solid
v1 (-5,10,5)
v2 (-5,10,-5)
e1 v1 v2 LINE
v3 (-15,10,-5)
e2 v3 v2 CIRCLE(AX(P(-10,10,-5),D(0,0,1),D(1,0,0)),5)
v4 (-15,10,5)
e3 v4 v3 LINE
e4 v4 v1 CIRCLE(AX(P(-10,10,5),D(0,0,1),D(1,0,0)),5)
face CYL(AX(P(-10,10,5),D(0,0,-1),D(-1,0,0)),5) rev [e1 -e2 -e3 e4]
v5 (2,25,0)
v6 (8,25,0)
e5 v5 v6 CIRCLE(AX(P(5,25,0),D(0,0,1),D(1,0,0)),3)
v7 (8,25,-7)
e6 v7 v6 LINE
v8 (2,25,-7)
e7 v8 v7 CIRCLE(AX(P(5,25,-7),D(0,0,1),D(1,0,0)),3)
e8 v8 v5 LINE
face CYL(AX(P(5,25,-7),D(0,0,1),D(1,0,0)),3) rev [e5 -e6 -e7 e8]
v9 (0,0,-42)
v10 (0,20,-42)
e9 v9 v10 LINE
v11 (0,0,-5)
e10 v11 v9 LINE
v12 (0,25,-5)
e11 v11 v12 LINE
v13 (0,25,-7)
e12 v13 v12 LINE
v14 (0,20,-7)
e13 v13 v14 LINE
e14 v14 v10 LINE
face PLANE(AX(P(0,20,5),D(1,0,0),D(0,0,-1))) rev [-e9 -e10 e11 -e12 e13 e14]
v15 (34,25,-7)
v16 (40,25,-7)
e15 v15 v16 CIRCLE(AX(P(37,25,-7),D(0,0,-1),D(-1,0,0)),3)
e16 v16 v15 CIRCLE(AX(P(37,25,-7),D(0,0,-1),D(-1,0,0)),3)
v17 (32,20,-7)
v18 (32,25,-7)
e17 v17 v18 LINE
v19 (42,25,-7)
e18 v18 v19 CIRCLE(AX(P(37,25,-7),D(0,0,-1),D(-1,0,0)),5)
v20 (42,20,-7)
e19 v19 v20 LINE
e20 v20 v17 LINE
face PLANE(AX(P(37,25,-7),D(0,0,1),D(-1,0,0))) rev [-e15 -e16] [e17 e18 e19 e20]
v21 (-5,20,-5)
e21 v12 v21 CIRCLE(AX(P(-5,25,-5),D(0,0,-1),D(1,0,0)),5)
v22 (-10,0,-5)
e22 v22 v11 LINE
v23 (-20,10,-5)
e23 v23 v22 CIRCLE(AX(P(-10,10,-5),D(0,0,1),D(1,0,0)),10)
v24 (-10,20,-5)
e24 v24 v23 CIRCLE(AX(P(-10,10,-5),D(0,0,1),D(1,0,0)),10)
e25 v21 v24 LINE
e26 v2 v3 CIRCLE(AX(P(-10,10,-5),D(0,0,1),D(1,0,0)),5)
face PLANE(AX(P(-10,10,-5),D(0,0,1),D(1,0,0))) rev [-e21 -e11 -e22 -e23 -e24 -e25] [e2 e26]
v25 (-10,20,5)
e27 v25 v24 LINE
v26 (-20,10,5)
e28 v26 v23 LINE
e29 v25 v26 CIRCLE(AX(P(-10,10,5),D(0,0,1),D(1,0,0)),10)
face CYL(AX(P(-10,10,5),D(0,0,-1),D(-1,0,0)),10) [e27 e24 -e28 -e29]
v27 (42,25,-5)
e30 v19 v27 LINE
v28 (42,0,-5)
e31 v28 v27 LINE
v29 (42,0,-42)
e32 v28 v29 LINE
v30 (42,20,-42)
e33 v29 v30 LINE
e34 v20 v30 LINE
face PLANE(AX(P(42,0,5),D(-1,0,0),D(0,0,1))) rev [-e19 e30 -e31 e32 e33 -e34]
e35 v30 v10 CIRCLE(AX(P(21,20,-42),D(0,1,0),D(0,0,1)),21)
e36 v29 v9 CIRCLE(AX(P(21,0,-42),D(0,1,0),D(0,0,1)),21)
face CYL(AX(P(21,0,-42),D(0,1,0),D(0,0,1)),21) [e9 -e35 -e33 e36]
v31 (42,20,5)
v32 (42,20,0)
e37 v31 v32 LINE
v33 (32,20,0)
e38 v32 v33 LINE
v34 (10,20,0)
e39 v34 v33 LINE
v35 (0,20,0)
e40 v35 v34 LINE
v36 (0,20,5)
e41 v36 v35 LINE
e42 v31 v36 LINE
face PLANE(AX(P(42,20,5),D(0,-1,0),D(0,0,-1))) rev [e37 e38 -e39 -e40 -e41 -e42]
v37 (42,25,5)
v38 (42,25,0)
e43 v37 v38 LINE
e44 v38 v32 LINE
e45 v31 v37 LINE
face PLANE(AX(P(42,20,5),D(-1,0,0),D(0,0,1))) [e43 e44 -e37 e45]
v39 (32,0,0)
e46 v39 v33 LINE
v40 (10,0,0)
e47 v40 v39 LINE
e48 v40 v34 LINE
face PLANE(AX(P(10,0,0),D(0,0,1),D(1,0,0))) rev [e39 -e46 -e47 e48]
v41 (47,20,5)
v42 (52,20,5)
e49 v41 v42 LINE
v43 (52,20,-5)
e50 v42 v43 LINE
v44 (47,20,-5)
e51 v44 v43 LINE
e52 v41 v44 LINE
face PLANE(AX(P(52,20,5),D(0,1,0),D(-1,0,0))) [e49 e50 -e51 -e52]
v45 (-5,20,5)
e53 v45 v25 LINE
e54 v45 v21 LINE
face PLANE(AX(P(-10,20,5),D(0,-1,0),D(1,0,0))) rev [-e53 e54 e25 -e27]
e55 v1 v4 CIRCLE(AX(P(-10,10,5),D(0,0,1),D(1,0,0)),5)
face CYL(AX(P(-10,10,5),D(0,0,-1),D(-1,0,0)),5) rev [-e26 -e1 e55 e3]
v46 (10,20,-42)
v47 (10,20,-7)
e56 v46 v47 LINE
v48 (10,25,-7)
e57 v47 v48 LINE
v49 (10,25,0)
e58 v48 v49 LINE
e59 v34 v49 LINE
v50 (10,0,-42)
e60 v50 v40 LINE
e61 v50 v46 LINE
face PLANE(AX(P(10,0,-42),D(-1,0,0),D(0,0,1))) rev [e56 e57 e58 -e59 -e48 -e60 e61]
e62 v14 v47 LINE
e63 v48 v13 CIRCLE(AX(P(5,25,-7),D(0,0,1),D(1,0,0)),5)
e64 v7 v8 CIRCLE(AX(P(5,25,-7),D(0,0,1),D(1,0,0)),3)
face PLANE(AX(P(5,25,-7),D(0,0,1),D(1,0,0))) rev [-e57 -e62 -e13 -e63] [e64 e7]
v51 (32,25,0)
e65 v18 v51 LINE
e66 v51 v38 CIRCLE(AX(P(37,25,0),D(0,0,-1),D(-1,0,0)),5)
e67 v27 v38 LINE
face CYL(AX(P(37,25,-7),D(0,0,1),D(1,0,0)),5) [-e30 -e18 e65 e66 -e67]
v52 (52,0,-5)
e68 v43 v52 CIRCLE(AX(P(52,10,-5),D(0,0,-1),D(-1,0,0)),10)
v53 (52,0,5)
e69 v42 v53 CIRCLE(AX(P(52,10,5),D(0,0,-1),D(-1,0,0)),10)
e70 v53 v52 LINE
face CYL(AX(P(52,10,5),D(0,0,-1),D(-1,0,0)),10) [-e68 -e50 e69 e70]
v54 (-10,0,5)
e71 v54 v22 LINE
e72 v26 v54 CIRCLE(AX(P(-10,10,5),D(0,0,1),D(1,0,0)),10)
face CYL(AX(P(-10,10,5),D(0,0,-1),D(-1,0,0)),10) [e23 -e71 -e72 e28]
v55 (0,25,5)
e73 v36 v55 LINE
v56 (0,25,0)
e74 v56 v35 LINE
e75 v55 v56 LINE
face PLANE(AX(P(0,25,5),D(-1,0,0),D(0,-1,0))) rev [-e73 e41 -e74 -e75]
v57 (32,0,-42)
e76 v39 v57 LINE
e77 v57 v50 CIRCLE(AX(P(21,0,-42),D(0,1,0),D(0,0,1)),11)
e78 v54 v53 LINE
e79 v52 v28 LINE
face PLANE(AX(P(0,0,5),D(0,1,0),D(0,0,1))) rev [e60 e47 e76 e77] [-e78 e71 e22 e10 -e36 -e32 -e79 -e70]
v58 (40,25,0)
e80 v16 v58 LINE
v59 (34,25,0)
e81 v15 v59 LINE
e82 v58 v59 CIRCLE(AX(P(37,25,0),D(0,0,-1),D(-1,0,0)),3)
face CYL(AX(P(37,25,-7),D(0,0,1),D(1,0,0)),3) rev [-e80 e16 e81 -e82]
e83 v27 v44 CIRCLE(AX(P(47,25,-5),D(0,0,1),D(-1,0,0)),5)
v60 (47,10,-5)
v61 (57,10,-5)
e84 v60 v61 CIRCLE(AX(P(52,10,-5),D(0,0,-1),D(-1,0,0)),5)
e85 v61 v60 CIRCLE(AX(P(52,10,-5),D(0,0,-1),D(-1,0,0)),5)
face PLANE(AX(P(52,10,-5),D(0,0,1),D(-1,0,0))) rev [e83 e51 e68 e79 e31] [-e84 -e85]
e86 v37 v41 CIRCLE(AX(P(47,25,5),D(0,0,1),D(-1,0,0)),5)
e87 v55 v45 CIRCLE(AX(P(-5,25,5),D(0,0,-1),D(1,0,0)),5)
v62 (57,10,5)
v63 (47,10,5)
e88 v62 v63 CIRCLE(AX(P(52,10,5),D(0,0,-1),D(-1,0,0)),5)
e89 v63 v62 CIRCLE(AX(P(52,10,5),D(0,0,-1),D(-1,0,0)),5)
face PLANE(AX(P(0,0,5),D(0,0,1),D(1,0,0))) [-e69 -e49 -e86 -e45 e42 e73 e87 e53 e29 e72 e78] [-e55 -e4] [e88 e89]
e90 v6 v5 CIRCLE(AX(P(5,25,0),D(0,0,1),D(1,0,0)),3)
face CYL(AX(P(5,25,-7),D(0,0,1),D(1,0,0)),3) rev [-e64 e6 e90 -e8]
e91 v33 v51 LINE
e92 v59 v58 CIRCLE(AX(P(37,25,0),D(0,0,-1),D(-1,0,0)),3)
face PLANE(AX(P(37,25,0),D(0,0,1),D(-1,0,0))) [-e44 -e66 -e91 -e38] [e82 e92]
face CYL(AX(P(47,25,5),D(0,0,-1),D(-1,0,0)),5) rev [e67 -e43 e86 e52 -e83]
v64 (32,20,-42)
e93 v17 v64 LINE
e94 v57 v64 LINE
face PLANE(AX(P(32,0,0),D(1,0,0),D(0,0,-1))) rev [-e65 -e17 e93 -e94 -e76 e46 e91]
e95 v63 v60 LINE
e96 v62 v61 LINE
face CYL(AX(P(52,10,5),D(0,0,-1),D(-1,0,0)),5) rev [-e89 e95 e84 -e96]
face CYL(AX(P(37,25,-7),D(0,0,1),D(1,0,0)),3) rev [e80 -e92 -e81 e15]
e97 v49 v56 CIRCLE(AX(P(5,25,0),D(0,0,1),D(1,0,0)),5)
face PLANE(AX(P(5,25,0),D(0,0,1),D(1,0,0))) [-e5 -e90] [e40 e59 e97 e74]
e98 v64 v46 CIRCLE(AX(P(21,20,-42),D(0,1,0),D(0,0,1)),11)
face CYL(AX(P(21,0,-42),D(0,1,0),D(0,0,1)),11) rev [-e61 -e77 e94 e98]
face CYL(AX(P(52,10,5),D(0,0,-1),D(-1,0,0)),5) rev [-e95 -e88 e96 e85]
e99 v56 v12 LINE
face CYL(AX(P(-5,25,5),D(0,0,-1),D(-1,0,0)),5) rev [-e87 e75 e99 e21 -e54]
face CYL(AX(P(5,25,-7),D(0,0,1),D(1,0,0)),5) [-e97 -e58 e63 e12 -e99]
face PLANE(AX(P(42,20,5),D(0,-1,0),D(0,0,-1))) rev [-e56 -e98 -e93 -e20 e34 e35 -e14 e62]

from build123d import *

# Parameters (mm, degrees)
BASE_PLATE_SKETCH_W    = 42
BASE_PLATE_SKETCH_H    = 20
BASE_PLATE_DEPTH       = 5
CURVED_LOOP_BOSS_DEPTH = 20
LOOP_SLOT_CUT_DEPTH    = 79.31347266
LUG_SKETCH_R           = 3
LUG_BOSS_DEPTH         = 7
PIN_EYE_SKETCH_R       = 5
PIN_EYE_BOSS_DEPTH     = 5


with BuildPart() as part:
    # Base Plate Sketch → Base Plate (new body)
    with BuildSketch(Plane.XY):
        with Locations((21, 10)):
            Rectangle(BASE_PLATE_SKETCH_W, BASE_PLATE_SKETCH_H)
    extrude(amount=BASE_PLATE_DEPTH)

    # Curved Loop Sketch → Curved Loop Boss (add, through all)
    with BuildSketch(Plane(origin=(0, 20, 0), x_dir=(1, 0, 0), z_dir=(0, 1, 0))):
        with BuildLine():
            Line((0, 42), (0, 0))
            Line((0, 0), (42, 0))
            Line((42, 0), (42, 42))
            ThreePointArc((42, 42), (21, 63), (0, 42))
        make_face()
    extrude(amount=-CURVED_LOOP_BOSS_DEPTH)

    # Loop Slot Sketch → Loop Slot Cut (cut, through all)
    with BuildSketch(Plane(origin=(0, 20, 0), x_dir=(1, 0, 0), z_dir=(0, 1, 0))):
        with BuildLine():
            Line((10, 42), (10, 0))
            Line((10, 0), (32, 0))
            Line((32, 0), (32, 42))
            ThreePointArc((32, 42), (21, 53), (10, 42))
        make_face()
    extrude(amount=-LOOP_SLOT_CUT_DEPTH, mode=Mode.SUBTRACT)

    # Lug Sketch → Lug Boss (add)
    with BuildSketch(Plane.XY):
        with BuildLine():
            Line((0, 25), (0, 20))
            Line((0, 20), (10, 20))
            Line((10, 20), (10, 25))
            ThreePointArc((10, 25), (5, 30), (0, 25))
        make_face()
        with Locations((5, 25)):
            Circle(LUG_SKETCH_R, mode=Mode.SUBTRACT)
    lug_boss = extrude(amount=-LUG_BOSS_DEPTH)

    # Lug Mirror: Lug Boss across plane
    add(lug_boss.mirror(Plane(origin=(21, 0, 0), x_dir=(0, 0, 1), z_dir=(1, 0, 0))))

    # Pin Eye Sketch → Pin Eye Boss (add, symmetric)
    with BuildSketch(Plane.XY):
        with BuildLine():
            Line((-10, 20), (-5, 20))
            ThreePointArc((-5, 20), (-1.464466094, 21.464466094), (0, 25))
            Line((0, 25), (0, 20))
            Line((0, 20), (0, 0))
            Line((0, 0), (-10, 0))
            ThreePointArc((-10, 0), (-20, 10), (-10, 20))
        make_face()
        with Locations((-10, 10)):
            Circle(PIN_EYE_SKETCH_R, mode=Mode.SUBTRACT)
    pin_eye_boss = extrude(amount=PIN_EYE_BOSS_DEPTH, both=True)

    # Pin Eye Mirror: Pin Eye Boss across plane
    add(pin_eye_boss.mirror(Plane(origin=(21, 0, 0), x_dir=(0, 0, 1), z_dir=(1, 0, 0))))


solid = part.part
